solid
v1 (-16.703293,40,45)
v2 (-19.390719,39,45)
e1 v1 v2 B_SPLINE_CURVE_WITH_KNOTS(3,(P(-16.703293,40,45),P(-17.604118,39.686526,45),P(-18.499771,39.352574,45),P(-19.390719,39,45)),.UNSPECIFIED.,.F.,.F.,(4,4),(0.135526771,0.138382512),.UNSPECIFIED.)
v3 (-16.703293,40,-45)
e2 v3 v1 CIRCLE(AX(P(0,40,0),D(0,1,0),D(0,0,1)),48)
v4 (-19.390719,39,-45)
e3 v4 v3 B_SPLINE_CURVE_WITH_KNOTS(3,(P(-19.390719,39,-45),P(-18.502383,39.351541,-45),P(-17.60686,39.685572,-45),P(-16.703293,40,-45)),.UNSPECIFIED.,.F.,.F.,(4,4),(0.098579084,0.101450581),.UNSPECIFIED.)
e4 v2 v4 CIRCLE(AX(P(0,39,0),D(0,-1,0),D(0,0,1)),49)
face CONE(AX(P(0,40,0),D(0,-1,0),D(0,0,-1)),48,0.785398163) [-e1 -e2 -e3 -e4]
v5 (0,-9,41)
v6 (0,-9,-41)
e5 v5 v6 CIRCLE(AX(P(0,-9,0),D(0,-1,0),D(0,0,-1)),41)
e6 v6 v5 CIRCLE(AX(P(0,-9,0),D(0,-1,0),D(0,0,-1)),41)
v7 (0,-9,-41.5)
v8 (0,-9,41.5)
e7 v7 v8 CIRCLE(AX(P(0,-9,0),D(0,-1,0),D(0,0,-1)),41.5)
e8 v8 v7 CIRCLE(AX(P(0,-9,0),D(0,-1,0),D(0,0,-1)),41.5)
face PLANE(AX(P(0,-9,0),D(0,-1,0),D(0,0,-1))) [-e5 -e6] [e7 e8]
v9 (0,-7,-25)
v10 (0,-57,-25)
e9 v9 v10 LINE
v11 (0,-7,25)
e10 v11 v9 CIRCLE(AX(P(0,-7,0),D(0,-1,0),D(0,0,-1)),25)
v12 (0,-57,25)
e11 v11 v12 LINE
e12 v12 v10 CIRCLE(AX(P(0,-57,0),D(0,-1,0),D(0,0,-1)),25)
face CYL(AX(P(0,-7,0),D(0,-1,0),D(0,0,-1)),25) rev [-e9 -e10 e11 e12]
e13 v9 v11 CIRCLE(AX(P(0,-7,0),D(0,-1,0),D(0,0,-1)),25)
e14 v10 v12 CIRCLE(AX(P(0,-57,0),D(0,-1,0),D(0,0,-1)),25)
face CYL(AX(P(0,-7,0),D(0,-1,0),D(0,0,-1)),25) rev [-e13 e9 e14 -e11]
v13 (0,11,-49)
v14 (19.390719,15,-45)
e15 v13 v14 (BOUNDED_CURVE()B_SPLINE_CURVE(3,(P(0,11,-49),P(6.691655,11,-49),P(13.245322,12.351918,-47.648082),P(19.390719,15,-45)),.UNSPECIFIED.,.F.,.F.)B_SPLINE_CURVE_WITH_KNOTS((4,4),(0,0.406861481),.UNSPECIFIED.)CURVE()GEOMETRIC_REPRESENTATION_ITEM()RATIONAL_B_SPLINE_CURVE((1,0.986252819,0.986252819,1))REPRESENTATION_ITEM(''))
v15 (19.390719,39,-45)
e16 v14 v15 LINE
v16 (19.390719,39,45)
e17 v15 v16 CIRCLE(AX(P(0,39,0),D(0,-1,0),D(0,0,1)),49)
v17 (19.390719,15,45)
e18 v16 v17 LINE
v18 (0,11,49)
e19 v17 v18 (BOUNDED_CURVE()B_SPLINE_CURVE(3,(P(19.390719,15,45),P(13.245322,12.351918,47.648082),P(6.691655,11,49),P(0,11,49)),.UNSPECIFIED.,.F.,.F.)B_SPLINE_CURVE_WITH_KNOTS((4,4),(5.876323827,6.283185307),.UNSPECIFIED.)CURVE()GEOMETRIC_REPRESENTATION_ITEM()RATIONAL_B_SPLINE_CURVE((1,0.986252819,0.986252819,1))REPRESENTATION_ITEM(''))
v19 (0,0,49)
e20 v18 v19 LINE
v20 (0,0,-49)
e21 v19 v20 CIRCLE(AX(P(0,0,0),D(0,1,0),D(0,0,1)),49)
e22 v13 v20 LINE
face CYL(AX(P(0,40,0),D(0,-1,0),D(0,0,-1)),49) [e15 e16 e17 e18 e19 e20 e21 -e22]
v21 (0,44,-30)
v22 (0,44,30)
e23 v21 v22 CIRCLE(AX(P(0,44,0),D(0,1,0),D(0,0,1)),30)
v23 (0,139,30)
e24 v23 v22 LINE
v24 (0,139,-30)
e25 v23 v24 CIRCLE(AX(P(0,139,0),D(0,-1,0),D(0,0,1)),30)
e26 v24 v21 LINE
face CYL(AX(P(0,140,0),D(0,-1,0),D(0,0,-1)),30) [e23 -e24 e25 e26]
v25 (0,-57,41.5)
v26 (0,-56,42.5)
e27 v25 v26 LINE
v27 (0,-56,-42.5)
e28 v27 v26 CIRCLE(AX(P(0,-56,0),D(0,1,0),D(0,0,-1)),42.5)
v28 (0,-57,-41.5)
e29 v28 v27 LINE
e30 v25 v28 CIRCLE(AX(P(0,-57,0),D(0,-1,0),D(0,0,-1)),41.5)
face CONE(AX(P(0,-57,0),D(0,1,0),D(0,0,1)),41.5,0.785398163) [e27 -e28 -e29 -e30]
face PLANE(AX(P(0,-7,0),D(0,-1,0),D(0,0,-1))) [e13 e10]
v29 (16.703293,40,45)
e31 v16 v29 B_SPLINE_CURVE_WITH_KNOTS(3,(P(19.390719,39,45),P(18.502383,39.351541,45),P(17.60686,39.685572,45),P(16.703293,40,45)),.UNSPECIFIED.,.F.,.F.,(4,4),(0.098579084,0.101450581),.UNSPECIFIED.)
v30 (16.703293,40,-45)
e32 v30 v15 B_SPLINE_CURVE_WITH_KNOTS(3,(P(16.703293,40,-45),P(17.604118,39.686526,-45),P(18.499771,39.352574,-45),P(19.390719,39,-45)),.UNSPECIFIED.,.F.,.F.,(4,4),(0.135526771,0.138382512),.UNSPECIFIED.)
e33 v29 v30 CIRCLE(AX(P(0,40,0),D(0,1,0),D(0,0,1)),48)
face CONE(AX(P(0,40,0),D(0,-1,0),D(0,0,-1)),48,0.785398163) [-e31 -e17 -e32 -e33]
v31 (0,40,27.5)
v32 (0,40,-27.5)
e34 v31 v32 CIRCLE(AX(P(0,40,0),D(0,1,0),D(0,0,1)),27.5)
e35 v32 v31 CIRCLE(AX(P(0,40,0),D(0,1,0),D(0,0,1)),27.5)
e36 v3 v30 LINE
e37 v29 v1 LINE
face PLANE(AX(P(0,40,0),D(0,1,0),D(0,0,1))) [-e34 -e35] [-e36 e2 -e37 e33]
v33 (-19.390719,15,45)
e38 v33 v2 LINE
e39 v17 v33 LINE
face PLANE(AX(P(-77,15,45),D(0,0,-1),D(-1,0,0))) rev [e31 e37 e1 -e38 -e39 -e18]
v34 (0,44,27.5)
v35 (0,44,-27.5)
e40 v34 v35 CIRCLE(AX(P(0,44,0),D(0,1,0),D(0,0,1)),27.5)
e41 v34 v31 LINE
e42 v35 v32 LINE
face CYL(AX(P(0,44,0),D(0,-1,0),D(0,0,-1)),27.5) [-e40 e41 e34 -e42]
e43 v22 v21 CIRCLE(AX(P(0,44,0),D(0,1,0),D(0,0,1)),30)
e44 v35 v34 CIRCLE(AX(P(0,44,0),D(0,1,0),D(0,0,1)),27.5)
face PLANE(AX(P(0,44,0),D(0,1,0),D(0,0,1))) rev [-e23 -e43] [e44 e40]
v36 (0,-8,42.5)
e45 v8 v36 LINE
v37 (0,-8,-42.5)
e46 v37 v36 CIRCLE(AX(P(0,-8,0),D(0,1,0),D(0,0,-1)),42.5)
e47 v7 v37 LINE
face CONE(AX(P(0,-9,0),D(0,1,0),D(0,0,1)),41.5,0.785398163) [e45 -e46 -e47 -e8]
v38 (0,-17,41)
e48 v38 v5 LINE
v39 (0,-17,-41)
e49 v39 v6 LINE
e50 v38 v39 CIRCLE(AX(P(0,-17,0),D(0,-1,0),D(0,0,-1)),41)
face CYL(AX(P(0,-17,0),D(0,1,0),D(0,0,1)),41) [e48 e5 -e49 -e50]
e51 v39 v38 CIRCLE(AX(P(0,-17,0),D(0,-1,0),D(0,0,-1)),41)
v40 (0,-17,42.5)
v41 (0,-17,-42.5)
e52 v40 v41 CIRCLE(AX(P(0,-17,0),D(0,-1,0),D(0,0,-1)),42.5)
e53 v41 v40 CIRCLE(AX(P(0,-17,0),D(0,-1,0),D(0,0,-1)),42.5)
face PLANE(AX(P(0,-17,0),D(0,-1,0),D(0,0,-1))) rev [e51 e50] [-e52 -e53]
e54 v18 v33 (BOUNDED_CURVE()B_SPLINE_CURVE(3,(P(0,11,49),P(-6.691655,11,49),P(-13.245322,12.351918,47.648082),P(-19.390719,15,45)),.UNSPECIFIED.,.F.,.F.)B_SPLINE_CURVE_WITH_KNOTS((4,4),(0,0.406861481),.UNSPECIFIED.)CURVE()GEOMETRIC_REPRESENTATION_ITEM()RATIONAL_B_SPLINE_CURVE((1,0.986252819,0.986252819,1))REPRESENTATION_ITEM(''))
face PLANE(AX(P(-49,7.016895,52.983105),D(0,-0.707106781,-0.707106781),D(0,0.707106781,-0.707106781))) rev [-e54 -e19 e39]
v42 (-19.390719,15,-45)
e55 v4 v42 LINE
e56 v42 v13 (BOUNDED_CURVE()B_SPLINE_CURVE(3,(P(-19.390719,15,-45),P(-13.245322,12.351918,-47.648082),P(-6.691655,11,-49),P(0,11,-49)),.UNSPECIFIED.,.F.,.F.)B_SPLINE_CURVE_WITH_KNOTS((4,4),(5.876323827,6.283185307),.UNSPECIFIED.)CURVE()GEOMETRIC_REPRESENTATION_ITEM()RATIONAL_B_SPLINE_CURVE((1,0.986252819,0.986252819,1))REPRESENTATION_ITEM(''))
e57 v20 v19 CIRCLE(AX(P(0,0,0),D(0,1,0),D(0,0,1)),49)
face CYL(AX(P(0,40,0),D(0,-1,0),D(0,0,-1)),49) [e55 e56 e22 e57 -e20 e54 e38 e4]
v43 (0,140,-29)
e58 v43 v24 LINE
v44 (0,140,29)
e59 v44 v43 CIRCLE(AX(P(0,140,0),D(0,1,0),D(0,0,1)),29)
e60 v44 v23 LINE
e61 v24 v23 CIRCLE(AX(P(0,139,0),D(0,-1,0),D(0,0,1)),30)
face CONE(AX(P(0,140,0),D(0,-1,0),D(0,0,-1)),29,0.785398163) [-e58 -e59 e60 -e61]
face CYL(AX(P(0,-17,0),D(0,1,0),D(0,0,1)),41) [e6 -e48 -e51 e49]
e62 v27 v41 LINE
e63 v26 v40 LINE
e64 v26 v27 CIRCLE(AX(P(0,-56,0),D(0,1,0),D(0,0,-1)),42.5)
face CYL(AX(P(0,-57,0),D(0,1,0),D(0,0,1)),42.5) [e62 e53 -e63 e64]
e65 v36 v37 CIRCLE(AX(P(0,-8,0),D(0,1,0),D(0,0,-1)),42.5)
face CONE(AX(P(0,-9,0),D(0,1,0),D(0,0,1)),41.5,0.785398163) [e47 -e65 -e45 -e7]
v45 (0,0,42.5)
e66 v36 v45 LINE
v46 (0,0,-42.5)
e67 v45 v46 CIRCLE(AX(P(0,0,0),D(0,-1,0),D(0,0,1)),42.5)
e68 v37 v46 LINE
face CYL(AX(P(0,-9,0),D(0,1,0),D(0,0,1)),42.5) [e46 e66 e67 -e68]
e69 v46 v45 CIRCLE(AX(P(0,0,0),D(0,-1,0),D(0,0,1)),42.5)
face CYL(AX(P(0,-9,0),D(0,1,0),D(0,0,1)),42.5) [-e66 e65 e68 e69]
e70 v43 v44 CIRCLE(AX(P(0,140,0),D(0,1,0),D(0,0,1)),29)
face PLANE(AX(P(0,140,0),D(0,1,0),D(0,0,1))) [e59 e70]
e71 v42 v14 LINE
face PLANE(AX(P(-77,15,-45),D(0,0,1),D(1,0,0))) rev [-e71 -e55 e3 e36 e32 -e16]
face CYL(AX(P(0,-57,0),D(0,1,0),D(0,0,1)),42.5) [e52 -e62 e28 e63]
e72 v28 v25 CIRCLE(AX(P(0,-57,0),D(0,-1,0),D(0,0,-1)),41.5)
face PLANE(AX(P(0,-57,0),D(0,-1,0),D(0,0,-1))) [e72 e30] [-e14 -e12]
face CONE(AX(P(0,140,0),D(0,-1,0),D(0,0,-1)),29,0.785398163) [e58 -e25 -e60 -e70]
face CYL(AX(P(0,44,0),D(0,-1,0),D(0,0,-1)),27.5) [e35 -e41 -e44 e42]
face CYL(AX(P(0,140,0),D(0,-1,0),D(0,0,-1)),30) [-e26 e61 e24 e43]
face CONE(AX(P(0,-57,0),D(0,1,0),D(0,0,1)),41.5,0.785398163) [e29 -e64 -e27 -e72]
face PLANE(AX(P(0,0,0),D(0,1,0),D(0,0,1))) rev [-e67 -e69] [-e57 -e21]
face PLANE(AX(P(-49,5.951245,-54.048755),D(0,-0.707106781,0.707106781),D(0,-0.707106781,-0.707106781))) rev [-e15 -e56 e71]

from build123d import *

# Parameters (mm, degrees)
SKETCH1_R           = 49
BOSS_EXTRUDE1_DEPTH = 40
SKETCH2_R           = 30
BOSS_EXTRUDE2_DEPTH = 100
SKETCH3_R           = 42.5
BOSS_EXTRUDE3_DEPTH = 9
SKETCH4_R           = 41
BOSS_EXTRUDE4_DEPTH = 8
SKETCH5_R           = 42.5
BOSS_EXTRUDE5_DEPTH = 40
CHAMFER1_SIZE       = 1
SKETCH6_W           = 154
SKETCH6_H           = 25
CUT_EXTRUDE1_DEPTH  = 25
CUT_EXTRUDE4_DEPTH  = 157.211395231
CUT_EXTRUDE5_DEPTH  = 157.211395231
SKETCH10_R          = 60.311534853
SKETCH10_R_2        = 27.5
CUT_EXTRUDE6_DEPTH  = 4
SKETCH13_R          = 25
CUT_EXTRUDE7_DEPTH  = 50


with BuildPart() as part:
    # Sketch1 → Boss-Extrude1 (new body)
    with BuildSketch(Plane(origin=(0, 0, 0), x_dir=(1, 0, 0), z_dir=(0, 1, 0))):
        with Locations(Location((0, 0, 0), (0, 0, 270))):
            Circle(SKETCH1_R)
    extrude(amount=BOSS_EXTRUDE1_DEPTH)

    # Sketch2 → Boss-Extrude2 (add)
    with BuildSketch(Plane(origin=(0, 40, 0), x_dir=(1, 0, 0), z_dir=(0, 1, 0))):
        with Locations(Location((0, 0, 0), (0, 0, 270))):
            Circle(SKETCH2_R)
    extrude(amount=BOSS_EXTRUDE2_DEPTH)

    # Sketch3 → Boss-Extrude3 (add)
    with BuildSketch(Plane.XZ):
        with Locations(Location((0, 0, 0), (0, 0, 90))):
            Circle(SKETCH3_R)
    extrude(amount=BOSS_EXTRUDE3_DEPTH)

    # Sketch4 → Boss-Extrude4 (add)
    with BuildSketch(Plane.XZ.offset(9)):
        with Locations(Location((0, 0, 0), (0, 0, 270))):
            Circle(SKETCH4_R)
    extrude(amount=BOSS_EXTRUDE4_DEPTH)

    # Sketch5 → Boss-Extrude5 (add)
    with BuildSketch(Plane.XZ.offset(17)):
        with Locations(Location((0, 0, 0), (0, 0, 90))):
            Circle(SKETCH5_R)
    extrude(amount=BOSS_EXTRUDE5_DEPTH)

    # Chamfer1
    chamfer1_edges = [part.edges().sort_by_distance(p)[0] for p in [
        (0, -9, -42.5),
        (0, -57, -42.5),
        (0, 40, -49),
        (0, 140, -30),
    ]]
    chamfer(chamfer1_edges, length=CHAMFER1_SIZE)

    # Sketch6 → Cut-Extrude1 (cut)
    with BuildSketch(Plane(origin=(0, 40, 0), x_dir=(1, 0, 0), z_dir=(0, 1, 0))):
        with Locations((0, 57.5)):
            Rectangle(SKETCH6_W, SKETCH6_H)
        with Locations((0, -57.5)):
            Rectangle(SKETCH6_W, SKETCH6_H)
    extrude(amount=-CUT_EXTRUDE1_DEPTH, mode=Mode.SUBTRACT)

    # Sketch 9_2 → Cut-Extrude4 (cut, through all)
    with BuildSketch(Plane(origin=(0, 0, 0), x_dir=(0, 0, -1), z_dir=(1, 0, 0))):
        Polygon((-45, 15), (-52.848399212, 15), (-52.983105111, 7.016894889), align=None)
        Polygon((45, 15), (54.94145121, 15), (54.048754667, 5.951245333), align=None)
    extrude(amount=-CUT_EXTRUDE4_DEPTH, mode=Mode.SUBTRACT)

    # Sketch 9_2 2 → Cut-Extrude5 (cut, through all)
    with BuildSketch(Plane(origin=(0, 0, 0), x_dir=(0, 0, -1), z_dir=(1, 0, 0))):
        Polygon((-45, 15), (-52.848399212, 15), (-52.983105111, 7.016894889), align=None)
        Polygon((45, 15), (54.94145121, 15), (54.048754667, 5.951245333), align=None)
    extrude(amount=CUT_EXTRUDE5_DEPTH, mode=Mode.SUBTRACT)

    # Sketch10 → Cut-Extrude6 (cut)
    with BuildSketch(Plane(origin=(0, 40, 0), x_dir=(1, 0, 0), z_dir=(0, 1, 0))):
        Circle(SKETCH10_R)
        with Locations(Location((0, 0, 0), (0, 0, 270))):
            Circle(SKETCH10_R_2, mode=Mode.SUBTRACT)
    extrude(amount=CUT_EXTRUDE6_DEPTH, mode=Mode.SUBTRACT)

    # Sketch13 → Cut-Extrude7 (cut)
    with BuildSketch(Plane.XZ.offset(57)):
        with Locations(Location((0, 0, 0), (0, 0, 270))):
            Circle(SKETCH13_R)
    extrude(amount=-CUT_EXTRUDE7_DEPTH, mode=Mode.SUBTRACT)


solid = part.part
